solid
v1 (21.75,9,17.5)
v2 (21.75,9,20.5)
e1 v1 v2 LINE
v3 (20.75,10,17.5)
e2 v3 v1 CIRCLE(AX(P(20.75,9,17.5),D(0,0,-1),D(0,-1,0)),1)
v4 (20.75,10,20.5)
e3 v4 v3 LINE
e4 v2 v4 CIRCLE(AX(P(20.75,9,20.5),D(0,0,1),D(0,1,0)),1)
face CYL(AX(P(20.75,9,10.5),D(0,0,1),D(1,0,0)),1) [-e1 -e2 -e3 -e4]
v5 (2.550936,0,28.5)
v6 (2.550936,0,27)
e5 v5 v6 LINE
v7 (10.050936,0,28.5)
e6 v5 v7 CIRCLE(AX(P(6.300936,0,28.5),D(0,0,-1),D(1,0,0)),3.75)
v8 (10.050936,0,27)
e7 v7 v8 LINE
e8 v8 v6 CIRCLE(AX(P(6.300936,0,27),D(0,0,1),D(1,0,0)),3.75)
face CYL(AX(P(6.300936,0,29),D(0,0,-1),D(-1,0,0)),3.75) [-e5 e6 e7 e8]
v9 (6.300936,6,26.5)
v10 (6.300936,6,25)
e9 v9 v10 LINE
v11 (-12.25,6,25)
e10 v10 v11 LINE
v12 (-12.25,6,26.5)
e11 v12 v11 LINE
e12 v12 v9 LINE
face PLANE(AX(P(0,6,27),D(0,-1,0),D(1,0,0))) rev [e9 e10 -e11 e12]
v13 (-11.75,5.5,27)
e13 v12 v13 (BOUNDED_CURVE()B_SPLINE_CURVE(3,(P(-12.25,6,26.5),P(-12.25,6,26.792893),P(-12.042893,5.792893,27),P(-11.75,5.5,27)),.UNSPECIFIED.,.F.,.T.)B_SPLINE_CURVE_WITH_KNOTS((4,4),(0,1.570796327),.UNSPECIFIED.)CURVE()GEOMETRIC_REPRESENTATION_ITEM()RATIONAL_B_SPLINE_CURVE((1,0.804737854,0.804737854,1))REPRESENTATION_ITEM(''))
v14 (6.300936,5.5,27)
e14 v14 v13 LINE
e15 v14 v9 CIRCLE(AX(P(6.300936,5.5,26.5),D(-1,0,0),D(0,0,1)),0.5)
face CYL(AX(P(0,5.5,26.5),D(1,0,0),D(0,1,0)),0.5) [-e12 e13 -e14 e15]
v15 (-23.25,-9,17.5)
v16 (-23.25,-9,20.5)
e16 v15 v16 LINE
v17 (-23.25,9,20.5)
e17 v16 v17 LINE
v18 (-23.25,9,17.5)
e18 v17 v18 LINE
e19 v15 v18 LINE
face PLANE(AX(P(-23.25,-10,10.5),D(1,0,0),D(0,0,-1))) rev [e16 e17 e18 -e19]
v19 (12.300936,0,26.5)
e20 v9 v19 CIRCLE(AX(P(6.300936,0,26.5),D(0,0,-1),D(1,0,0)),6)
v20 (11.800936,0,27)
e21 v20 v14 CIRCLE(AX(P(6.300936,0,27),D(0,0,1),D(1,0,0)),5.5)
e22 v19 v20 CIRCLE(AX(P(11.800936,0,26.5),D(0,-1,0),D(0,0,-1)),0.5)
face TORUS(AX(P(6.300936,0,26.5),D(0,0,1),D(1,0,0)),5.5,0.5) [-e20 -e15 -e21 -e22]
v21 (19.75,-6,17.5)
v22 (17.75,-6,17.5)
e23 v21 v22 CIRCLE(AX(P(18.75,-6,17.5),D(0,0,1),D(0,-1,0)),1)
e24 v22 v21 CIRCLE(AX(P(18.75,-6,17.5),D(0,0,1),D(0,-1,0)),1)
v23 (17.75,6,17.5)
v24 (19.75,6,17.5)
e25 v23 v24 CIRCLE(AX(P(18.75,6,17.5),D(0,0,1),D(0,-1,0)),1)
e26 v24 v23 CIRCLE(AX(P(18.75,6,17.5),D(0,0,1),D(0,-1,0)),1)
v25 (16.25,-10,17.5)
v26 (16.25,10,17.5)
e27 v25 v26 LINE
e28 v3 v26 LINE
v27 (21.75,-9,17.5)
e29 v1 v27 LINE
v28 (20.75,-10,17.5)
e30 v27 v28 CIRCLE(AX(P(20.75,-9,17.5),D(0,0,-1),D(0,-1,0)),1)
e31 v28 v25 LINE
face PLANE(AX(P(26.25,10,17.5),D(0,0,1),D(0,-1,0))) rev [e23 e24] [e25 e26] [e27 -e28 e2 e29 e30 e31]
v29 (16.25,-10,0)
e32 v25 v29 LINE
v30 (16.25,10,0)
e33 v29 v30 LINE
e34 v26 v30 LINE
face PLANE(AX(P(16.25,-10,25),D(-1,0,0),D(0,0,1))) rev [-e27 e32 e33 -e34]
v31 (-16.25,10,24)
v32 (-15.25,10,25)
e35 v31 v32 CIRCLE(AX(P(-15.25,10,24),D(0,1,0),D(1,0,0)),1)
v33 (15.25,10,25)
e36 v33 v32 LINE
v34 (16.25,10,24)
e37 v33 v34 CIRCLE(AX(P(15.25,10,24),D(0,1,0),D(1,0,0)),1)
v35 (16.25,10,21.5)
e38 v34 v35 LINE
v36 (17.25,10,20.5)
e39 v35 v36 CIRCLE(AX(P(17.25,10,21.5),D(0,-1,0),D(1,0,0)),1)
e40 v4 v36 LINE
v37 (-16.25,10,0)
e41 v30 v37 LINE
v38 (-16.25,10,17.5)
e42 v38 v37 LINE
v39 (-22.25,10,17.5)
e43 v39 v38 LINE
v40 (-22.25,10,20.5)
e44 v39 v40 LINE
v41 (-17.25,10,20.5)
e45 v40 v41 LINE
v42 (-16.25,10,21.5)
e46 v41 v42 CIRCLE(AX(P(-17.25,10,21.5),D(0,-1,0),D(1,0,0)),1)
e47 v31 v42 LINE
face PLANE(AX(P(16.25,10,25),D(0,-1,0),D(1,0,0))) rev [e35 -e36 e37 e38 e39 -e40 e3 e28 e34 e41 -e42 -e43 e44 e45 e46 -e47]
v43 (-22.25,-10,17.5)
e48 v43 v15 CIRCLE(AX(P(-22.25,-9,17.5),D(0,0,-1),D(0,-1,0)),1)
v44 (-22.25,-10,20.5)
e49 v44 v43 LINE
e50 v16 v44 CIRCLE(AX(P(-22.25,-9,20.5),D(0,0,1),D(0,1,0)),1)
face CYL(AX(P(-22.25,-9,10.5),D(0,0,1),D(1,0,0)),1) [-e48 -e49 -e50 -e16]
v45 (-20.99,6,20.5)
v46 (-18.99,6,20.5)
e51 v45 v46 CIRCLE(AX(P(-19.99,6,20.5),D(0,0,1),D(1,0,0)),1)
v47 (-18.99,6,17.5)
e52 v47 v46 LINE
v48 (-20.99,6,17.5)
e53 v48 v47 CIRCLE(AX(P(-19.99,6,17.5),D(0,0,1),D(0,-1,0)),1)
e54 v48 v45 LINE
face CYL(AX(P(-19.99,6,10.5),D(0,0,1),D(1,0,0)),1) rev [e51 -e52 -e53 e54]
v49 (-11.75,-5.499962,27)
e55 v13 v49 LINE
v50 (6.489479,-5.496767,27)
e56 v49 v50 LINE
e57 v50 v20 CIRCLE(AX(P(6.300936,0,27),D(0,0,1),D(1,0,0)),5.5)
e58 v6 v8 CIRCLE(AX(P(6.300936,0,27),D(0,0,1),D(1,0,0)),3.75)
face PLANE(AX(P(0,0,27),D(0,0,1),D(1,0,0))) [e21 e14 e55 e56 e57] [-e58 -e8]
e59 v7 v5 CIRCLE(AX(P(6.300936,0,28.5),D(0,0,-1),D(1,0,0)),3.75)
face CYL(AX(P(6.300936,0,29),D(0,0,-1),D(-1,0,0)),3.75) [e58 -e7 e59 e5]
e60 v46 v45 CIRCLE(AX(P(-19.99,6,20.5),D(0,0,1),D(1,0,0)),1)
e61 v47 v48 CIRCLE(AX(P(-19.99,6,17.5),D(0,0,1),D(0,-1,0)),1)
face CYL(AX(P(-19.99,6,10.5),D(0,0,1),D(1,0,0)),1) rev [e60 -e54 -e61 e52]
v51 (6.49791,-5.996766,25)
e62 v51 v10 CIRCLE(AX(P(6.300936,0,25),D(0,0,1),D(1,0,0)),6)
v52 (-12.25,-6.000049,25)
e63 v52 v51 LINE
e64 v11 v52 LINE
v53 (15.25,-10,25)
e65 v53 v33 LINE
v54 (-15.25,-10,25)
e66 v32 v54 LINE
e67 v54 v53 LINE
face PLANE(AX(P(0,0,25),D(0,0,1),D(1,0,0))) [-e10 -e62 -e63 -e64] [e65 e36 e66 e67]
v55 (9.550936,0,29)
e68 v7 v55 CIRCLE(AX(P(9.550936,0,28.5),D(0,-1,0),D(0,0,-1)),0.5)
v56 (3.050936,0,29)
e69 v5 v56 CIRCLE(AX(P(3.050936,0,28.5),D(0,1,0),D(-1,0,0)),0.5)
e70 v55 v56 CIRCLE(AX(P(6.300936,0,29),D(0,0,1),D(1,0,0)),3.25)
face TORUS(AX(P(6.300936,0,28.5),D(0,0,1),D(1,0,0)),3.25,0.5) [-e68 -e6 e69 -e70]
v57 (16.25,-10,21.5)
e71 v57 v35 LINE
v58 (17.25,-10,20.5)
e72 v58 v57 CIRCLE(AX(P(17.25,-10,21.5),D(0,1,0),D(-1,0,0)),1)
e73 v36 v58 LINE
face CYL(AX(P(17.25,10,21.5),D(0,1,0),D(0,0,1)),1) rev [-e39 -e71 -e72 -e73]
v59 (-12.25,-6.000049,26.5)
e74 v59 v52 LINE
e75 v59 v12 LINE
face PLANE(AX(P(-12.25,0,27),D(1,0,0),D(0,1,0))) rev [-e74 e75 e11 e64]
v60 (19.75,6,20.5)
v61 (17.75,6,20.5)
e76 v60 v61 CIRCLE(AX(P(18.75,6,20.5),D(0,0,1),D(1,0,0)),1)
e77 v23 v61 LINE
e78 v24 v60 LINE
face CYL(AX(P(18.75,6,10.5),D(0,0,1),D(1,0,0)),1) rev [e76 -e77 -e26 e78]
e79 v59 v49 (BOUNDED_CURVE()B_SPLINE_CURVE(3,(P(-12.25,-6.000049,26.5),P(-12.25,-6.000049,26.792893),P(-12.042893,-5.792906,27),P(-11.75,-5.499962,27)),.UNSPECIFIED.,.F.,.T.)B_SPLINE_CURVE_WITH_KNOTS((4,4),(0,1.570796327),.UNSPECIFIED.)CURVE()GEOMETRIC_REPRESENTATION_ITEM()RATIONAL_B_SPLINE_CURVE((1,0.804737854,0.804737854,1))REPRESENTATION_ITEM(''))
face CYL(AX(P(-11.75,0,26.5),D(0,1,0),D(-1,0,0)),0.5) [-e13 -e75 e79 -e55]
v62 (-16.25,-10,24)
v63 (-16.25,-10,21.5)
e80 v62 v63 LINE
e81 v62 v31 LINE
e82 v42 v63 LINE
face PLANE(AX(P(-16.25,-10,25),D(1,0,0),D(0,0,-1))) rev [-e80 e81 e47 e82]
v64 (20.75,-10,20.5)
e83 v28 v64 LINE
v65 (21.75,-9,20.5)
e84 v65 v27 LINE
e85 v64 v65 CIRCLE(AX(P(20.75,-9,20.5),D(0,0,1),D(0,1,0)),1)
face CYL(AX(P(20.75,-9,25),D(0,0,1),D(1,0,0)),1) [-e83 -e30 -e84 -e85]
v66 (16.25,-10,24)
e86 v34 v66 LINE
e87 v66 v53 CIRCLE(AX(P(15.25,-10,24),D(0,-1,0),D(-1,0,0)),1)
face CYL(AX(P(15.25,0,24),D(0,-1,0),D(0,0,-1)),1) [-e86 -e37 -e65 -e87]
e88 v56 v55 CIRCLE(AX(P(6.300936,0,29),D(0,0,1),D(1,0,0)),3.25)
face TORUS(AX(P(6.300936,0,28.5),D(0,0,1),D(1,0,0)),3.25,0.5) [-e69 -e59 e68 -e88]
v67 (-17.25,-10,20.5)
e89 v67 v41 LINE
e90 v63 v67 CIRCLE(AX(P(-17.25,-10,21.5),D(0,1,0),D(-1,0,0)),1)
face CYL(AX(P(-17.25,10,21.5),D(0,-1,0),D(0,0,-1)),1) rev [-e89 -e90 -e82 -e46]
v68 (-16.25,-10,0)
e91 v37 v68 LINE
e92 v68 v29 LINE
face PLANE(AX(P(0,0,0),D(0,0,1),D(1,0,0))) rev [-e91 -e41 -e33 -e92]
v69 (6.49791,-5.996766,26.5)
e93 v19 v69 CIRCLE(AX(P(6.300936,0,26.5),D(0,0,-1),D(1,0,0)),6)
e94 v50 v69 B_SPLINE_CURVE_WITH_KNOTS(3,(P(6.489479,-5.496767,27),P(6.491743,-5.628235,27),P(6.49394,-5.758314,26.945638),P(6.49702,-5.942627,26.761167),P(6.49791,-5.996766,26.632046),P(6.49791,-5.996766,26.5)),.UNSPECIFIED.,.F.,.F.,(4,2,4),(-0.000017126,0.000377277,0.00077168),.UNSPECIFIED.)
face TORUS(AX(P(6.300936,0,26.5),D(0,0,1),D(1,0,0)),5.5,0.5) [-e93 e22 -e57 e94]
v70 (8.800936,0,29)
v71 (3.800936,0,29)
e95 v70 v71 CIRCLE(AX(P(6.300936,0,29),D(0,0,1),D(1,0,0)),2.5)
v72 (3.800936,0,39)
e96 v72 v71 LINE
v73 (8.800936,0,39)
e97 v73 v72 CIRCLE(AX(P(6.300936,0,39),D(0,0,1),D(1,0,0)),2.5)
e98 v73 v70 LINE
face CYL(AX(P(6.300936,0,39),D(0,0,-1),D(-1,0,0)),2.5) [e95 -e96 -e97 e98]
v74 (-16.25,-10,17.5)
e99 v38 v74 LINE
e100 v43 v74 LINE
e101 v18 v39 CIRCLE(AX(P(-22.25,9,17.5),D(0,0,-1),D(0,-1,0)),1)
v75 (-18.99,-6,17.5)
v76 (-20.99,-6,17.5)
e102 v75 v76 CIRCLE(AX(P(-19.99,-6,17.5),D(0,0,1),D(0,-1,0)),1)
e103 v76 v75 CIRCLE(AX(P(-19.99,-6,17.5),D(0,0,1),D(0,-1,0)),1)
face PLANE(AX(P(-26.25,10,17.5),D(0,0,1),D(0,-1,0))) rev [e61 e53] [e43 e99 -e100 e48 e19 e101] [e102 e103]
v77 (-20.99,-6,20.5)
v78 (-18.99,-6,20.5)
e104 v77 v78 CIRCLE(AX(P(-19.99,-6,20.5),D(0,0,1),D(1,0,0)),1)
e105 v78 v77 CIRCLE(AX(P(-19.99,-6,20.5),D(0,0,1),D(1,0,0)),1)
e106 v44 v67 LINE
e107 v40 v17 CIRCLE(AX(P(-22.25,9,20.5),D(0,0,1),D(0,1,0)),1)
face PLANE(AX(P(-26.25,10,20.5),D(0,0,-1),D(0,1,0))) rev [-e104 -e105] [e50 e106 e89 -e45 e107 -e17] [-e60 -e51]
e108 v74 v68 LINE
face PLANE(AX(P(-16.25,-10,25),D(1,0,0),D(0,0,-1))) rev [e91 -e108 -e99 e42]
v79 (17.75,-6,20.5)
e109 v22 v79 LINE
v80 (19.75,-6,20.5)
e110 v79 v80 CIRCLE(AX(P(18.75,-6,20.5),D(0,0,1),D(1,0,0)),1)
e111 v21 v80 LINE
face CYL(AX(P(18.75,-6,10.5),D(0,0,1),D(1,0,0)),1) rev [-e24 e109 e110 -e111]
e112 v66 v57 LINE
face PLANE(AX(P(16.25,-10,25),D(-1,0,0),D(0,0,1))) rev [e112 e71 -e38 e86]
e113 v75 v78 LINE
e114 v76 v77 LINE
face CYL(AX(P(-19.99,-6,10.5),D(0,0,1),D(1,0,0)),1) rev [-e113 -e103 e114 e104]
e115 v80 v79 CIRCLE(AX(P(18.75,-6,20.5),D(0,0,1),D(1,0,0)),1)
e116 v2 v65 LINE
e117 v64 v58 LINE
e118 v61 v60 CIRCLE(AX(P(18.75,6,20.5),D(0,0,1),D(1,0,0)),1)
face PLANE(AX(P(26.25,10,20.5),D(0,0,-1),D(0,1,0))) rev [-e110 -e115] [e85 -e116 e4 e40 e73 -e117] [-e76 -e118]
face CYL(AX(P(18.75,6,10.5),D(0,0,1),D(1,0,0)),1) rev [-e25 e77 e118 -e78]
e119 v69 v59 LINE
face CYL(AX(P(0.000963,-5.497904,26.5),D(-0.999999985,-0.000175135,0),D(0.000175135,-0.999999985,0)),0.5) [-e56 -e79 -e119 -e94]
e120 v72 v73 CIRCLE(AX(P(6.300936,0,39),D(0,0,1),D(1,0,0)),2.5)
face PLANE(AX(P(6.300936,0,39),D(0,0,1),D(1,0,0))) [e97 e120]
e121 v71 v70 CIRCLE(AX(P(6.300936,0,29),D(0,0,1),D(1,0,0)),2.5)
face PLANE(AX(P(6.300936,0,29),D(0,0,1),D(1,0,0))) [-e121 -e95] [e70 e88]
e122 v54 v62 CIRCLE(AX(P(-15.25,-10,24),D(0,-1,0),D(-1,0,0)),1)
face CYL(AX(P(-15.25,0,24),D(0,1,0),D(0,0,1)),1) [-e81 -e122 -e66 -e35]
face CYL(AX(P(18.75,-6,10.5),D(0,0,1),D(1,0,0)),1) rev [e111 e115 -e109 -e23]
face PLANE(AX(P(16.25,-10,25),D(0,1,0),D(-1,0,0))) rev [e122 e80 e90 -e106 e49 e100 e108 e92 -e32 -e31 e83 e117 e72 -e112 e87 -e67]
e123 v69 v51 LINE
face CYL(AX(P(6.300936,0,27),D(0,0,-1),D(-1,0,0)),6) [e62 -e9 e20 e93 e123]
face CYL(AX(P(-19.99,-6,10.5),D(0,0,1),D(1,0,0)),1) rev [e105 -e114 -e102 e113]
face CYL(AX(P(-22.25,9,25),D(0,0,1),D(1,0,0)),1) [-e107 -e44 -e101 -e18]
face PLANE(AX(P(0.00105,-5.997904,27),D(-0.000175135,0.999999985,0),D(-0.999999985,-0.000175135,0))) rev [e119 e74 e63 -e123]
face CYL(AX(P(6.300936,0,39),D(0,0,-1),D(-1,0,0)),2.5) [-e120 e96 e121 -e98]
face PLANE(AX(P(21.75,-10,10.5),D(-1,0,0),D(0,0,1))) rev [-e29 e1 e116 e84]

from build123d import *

# Parameters (mm, degrees)
SKETCH1_W           = 65
SKETCH1_H           = 40
BOSS_EXTRUDE1_DEPTH = 50
BOSS_EXTRUDE2_DEPTH = 4
SKETCH3_R           = 7.5
BOSS_EXTRUDE3_DEPTH = 4
SKETCH4_R           = 5
BOSS_EXTRUDE4_DEPTH = 20
FILLET1_R           = 1
SKETCH5_W           = 6
SKETCH5_H           = 40
BOSS_EXTRUDE5_DEPTH = 20
SKETCH6_W           = 6
SKETCH6_H           = 40
BOSS_EXTRUDE6_DEPTH = 20
SKETCH7_R           = 2
SKETCH7_W           = 9
SKETCH7_H           = 40
SKETCH7_W_2         = 6
CUT_EXTRUDE1_DEPTH  = 20
FILLET2_R           = 2
SCALE1_SCALE        = 0.5


with BuildPart() as part:
    # Sketch1 → Boss-Extrude1 (new body)
    with BuildSketch(Plane.XY):
        Rectangle(SKETCH1_W, SKETCH1_H)
    extrude(amount=BOSS_EXTRUDE1_DEPTH)

    # Sketch2 → Boss-Extrude2 (add)
    with BuildSketch(Plane.XY.offset(50)):
        with BuildLine():
            ThreePointArc((12.995819527, -11.993531793), (24.600254242, 0.197000611), (12.601871402, 12))
            Line((12.601871402, 12), (-24.5, 12))
            Line((-24.5, 12), (-24.5, -12.000098614))
            Line((-24.5, -12.000098614), (12.21212427, -11.993669046))
            Line((12.21212427, -11.993669046), (12.995819527, -11.993531793))
        make_face()
    extrude(amount=BOSS_EXTRUDE2_DEPTH)

    # Sketch3 → Boss-Extrude3 (add)
    with BuildSketch(Plane.XY.offset(54)):
        with Locations((12.601871402, 0)):
            Circle(SKETCH3_R)
    extrude(amount=BOSS_EXTRUDE3_DEPTH)

    # Sketch4 → Boss-Extrude4 (add)
    with BuildSketch(Plane.XY.offset(58)):
        with Locations((12.601871402, 0)):
            Circle(SKETCH4_R)
    extrude(amount=BOSS_EXTRUDE4_DEPTH)

    # Fillet1
    fillet1_edges = [part.edges().sort_by_distance(p)[0] for p in [
        (-5.752090236, -11.996815204, 54),
        (24.600254242, 0.197000611, 54),
        (-5.949064299, 12, 54),
        (-24.5, -4.9307e-05, 54),
        (5.101871402, 0, 58),
    ]]
    fillet(fillet1_edges, radius=FILLET1_R)

    # Sketch5 → Boss-Extrude5 (add)
    with BuildSketch(Plane(origin=(32.5, 0, 0), x_dir=(0, 0, -1), z_dir=(1, 0, 0))):
        with Locations((-38, 0)):
            Rectangle(SKETCH5_W, SKETCH5_H)
    extrude(amount=BOSS_EXTRUDE5_DEPTH)

    # Sketch6 → Boss-Extrude6 (add)
    with BuildSketch(Plane.ZY.offset(32.5)):
        with Locations((38, 0)):
            Rectangle(SKETCH6_W, SKETCH6_H)
    extrude(amount=BOSS_EXTRUDE6_DEPTH)

    # Sketch7 → Cut-Extrude1 (cut)
    with BuildSketch(Plane.XY.offset(41)):
        with Locations((-39.98, 12)):
            Circle(SKETCH7_R)
        with Locations((-39.98, -12)):
            Circle(SKETCH7_R)
        with Locations((37.5, 12)):
            Circle(SKETCH7_R)
        with Locations((37.5, -12)):
            Circle(SKETCH7_R)
        with Locations((48, 0)):
            Rectangle(SKETCH7_W, SKETCH7_H)
        with Locations((-49.5, 0)):
            Rectangle(SKETCH7_W_2, SKETCH7_H)
    extrude(amount=-CUT_EXTRUDE1_DEPTH, mode=Mode.SUBTRACT)

    # Fillet2
    fillet2_edges = [part.edges().sort_by_distance(p)[0] for p in [
        (32.5, 0, 50),
        (-46.5, 20, 38),
        (-46.5, -20, 38),
        (-32.5, 0, 50),
        (32.5, 0, 41),
        (-32.5, 0, 41),
        (43.5, -20, 38),
        (43.5, 20, 38),
    ]]
    fillet(fillet2_edges, radius=FILLET2_R)


with BuildPart() as part_1:
    # Scale1: scaled about (0, 0, 0)
    add(part.part.scale(SCALE1_SCALE))


solid = part_1.part
